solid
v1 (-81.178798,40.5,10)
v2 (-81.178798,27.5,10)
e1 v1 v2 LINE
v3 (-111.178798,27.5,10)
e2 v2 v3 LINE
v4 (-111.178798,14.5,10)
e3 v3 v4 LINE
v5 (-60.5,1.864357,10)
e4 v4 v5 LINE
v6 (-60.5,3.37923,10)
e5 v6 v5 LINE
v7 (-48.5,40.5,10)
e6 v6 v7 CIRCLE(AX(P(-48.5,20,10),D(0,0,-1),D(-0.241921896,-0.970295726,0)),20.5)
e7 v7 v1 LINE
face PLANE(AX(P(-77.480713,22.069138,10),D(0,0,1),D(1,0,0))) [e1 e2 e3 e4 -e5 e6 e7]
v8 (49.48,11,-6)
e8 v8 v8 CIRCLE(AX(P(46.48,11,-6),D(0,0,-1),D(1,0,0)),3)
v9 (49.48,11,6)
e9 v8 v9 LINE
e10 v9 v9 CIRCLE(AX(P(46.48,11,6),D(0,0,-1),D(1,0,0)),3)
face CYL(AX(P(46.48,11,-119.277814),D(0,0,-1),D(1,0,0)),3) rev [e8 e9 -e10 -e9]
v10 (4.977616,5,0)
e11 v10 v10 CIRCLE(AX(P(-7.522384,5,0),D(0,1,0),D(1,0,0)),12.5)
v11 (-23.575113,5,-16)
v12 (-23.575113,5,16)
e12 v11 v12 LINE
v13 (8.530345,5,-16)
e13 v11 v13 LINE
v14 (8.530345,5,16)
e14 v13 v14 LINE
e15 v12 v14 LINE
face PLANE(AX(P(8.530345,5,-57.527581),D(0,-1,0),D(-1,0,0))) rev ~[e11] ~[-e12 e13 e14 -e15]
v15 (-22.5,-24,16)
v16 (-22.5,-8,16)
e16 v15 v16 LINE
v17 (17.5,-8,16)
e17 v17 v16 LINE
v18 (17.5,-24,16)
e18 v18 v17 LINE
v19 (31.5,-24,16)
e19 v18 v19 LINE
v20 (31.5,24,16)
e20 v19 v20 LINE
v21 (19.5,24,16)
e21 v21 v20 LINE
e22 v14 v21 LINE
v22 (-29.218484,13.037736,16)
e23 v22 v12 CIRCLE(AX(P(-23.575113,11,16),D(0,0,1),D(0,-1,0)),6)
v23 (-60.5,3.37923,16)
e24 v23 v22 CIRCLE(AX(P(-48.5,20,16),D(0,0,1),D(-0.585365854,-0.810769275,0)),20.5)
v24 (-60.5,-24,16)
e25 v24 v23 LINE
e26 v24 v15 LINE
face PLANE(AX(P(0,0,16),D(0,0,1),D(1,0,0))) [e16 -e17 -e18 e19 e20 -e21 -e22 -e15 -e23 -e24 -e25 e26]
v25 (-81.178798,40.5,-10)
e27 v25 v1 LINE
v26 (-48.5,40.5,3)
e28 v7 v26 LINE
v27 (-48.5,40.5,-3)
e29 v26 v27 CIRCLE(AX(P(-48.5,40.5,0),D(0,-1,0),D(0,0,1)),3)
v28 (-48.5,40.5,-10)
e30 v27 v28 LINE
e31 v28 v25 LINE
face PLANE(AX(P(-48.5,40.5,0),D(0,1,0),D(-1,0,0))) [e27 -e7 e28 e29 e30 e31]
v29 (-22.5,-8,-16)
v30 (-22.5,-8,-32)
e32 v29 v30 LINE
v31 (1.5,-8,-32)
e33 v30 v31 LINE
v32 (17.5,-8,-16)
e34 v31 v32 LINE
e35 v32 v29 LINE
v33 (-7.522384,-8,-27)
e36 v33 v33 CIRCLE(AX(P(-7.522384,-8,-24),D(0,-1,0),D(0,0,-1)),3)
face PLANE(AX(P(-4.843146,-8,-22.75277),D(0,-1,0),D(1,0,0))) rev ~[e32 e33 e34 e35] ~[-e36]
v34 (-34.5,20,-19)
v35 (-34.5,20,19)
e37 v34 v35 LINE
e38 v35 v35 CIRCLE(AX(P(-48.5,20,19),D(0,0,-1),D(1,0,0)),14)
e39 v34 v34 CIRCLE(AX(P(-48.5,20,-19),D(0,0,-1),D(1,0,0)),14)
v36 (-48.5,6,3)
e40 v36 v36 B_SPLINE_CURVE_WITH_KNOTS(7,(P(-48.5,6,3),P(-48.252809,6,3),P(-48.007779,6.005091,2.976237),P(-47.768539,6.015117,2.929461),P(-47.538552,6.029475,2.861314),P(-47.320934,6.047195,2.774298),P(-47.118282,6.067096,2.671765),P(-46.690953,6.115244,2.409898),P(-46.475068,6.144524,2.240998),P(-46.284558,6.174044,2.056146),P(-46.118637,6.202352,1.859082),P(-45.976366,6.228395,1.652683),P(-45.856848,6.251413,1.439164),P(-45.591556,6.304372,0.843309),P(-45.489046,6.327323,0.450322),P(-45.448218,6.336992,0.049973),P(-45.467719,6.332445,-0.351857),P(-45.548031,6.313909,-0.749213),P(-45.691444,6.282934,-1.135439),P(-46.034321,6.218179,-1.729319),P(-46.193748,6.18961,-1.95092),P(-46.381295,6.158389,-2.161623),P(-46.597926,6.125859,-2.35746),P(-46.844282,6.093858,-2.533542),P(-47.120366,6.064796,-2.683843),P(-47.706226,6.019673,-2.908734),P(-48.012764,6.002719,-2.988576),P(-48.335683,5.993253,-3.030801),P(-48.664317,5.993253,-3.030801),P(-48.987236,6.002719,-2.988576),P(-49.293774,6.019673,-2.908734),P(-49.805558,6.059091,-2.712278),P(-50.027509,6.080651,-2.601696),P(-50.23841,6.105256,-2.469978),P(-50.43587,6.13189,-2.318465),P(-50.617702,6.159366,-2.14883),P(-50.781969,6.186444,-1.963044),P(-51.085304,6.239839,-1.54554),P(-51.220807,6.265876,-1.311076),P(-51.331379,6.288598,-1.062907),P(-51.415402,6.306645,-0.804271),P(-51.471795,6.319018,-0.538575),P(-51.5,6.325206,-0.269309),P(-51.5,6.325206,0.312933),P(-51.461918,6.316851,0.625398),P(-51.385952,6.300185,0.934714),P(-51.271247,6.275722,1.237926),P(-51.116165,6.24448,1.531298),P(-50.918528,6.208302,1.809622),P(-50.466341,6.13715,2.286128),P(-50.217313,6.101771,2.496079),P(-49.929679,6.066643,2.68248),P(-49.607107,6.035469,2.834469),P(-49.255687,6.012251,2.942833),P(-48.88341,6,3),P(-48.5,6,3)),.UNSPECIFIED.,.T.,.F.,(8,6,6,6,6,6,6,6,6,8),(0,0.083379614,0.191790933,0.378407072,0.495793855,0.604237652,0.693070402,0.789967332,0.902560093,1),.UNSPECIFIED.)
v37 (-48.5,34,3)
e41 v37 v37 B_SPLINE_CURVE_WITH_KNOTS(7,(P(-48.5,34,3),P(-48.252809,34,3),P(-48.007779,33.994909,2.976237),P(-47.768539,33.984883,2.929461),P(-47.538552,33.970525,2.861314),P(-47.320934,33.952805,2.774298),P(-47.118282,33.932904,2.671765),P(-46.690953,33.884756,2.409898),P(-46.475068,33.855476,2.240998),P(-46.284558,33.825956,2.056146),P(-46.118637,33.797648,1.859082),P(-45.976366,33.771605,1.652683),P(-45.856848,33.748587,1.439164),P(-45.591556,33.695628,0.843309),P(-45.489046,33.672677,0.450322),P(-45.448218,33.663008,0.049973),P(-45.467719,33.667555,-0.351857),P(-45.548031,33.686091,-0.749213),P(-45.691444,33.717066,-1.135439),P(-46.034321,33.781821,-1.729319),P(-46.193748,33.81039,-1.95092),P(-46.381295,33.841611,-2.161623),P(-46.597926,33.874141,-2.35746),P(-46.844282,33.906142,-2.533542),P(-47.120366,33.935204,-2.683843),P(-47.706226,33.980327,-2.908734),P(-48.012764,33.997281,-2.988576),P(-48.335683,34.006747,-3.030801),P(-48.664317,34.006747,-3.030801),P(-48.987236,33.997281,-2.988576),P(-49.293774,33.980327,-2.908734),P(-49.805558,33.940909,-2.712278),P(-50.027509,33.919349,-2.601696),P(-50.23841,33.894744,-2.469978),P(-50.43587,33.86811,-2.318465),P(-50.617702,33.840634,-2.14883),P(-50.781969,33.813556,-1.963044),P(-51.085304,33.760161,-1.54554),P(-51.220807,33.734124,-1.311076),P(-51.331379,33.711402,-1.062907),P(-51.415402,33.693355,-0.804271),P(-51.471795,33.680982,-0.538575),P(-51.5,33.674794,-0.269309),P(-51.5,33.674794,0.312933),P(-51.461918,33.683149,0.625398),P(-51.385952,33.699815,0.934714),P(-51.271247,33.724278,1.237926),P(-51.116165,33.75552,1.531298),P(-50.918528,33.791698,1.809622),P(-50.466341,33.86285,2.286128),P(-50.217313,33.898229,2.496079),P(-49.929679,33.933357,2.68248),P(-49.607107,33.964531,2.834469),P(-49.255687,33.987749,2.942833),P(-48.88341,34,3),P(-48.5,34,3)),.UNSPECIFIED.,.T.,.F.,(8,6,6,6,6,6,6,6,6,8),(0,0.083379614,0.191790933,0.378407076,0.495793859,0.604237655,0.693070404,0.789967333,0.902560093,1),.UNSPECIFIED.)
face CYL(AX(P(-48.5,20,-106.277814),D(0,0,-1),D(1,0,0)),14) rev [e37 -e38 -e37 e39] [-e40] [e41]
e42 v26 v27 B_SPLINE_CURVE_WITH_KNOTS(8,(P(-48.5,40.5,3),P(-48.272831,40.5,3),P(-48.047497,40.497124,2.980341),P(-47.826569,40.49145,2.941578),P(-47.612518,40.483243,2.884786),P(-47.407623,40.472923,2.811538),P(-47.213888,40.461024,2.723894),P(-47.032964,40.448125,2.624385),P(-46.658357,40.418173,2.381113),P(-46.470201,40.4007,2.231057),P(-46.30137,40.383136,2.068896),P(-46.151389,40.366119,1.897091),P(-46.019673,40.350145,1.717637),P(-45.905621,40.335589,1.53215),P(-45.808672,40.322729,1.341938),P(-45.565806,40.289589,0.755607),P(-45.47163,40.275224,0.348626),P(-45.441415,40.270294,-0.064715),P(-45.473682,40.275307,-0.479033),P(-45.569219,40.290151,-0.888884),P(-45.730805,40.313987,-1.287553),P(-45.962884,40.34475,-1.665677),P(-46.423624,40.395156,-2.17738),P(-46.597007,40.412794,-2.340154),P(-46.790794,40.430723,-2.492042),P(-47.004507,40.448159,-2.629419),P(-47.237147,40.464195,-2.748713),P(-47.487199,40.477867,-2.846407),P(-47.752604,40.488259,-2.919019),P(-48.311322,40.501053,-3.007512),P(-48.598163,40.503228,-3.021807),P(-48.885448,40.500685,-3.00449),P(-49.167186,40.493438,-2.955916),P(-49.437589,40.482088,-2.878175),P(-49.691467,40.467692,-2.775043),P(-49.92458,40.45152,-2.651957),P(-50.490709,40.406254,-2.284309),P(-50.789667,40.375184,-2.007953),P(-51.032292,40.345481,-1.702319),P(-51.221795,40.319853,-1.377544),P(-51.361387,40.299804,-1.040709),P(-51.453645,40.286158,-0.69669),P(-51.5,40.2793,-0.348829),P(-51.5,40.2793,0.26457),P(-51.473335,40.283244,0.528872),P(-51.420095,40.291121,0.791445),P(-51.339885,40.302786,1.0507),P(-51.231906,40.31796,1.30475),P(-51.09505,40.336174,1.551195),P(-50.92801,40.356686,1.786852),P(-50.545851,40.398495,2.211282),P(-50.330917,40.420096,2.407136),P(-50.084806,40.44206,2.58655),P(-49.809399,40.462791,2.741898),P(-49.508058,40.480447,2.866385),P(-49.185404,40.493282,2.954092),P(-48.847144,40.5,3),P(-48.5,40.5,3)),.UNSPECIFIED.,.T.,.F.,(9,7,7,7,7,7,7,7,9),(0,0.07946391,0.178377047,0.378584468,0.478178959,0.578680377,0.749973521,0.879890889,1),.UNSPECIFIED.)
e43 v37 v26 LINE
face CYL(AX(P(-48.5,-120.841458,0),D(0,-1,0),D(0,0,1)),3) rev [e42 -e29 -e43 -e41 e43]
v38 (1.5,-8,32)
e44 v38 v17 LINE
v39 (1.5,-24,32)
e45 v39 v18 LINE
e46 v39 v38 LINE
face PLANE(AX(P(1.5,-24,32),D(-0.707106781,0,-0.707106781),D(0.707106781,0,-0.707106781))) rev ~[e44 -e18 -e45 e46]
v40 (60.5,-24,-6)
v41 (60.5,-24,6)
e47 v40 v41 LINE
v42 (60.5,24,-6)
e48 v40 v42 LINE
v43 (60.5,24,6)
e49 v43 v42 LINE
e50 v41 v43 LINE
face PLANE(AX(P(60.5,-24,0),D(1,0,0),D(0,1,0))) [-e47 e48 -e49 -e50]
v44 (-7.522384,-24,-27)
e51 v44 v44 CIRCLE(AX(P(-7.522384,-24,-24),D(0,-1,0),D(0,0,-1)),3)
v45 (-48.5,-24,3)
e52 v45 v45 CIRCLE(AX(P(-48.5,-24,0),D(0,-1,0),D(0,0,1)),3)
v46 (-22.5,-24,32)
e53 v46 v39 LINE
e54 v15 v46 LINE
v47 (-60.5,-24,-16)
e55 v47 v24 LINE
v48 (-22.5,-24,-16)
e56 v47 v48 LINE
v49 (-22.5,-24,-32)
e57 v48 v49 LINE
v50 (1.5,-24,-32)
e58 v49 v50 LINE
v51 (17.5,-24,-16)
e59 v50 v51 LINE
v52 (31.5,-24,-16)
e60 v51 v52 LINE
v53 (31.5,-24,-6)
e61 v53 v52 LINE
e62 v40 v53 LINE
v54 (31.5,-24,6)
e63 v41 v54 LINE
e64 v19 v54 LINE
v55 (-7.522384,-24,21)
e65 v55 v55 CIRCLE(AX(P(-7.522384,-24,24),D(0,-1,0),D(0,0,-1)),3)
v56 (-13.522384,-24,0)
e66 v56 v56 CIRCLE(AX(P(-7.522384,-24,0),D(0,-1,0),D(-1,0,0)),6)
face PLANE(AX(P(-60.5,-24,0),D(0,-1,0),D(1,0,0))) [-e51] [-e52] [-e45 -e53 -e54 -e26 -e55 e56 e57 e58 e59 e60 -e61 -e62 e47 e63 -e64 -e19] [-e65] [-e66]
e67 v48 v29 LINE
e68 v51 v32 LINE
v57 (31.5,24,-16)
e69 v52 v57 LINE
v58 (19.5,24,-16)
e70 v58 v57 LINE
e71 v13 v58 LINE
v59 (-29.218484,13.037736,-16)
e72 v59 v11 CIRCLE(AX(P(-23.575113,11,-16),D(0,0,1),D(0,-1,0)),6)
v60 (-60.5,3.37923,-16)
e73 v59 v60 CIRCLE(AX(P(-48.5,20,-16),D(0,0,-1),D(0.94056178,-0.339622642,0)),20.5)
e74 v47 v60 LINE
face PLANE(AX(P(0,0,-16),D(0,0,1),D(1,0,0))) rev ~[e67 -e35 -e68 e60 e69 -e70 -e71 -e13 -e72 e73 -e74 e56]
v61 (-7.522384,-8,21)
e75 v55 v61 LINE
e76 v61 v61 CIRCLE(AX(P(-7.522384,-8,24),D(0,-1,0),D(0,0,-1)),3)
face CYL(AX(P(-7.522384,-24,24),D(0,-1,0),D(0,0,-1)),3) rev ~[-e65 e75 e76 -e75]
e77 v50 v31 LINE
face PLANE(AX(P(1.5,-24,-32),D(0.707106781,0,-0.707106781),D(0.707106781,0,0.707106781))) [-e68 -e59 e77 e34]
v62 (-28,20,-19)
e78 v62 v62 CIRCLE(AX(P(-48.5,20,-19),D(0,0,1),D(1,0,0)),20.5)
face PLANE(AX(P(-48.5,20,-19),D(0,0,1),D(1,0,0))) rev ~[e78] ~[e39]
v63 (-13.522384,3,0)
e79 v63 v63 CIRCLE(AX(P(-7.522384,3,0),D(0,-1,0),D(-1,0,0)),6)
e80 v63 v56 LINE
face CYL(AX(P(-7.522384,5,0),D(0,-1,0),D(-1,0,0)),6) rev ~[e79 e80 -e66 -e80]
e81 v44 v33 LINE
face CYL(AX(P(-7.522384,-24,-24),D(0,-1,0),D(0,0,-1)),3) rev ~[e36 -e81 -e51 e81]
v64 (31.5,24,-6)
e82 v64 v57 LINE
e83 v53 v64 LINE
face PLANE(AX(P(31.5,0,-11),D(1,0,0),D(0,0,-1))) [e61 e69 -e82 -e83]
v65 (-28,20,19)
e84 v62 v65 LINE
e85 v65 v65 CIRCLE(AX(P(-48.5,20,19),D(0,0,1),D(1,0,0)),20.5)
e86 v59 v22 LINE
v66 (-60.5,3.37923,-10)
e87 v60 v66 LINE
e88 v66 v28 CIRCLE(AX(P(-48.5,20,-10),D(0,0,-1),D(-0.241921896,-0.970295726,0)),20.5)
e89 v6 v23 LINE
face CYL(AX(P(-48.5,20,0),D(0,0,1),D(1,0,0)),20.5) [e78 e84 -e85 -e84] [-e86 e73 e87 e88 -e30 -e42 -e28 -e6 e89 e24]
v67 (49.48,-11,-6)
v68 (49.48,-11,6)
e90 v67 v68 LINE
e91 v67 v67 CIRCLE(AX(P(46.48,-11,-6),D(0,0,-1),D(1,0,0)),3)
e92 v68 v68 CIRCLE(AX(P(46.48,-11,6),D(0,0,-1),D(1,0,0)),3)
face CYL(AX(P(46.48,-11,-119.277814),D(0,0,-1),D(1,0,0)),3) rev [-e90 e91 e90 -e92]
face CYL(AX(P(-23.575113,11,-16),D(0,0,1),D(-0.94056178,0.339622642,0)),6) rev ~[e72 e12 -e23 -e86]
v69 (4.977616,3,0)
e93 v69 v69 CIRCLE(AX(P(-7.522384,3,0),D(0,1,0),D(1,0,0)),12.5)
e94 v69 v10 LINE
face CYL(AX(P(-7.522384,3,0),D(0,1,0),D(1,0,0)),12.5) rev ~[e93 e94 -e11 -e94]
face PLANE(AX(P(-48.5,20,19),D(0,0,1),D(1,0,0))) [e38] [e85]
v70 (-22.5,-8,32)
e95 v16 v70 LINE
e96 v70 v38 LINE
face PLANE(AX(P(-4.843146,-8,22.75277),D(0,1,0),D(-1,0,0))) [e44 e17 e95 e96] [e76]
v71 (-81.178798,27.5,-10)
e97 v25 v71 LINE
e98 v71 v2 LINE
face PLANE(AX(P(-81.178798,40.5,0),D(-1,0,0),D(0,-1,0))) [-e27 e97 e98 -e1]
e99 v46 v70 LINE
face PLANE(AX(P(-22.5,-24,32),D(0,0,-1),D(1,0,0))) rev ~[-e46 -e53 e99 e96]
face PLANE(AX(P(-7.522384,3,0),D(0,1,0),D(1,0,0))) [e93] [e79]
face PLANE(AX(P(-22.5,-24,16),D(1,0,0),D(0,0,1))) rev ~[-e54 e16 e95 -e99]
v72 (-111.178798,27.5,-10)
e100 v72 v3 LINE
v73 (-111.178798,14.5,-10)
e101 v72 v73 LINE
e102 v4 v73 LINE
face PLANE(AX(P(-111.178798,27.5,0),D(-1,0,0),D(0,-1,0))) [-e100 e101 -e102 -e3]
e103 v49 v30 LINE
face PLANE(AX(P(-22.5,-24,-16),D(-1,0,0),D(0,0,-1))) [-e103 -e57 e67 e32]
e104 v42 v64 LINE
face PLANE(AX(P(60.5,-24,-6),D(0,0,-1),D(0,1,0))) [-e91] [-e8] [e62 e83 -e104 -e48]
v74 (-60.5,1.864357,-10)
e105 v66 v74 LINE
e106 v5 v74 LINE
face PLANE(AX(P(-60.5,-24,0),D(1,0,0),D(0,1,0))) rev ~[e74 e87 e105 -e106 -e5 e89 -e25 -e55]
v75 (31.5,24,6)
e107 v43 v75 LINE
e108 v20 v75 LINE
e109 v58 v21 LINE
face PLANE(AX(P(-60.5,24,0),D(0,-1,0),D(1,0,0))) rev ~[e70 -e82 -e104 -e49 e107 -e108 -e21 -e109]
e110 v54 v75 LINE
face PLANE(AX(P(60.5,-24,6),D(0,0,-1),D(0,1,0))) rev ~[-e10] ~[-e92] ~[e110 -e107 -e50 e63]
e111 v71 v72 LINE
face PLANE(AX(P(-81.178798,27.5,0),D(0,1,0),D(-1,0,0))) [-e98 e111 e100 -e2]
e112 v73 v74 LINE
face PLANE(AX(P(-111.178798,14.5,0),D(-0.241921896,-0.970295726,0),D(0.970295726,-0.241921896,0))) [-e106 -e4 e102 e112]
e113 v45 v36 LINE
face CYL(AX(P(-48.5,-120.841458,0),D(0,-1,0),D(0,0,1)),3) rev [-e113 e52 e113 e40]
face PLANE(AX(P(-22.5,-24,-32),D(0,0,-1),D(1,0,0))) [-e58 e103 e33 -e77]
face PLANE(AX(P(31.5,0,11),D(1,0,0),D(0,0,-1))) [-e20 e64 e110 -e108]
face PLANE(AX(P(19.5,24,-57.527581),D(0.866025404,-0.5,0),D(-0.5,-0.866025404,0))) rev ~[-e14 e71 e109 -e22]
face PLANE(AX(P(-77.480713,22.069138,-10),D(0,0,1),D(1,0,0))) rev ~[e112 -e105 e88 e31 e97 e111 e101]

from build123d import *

# Parameters (mm, degrees)
BASE_BLOCK_SKETCH_W                = 121
BASE_BLOCK_SKETCH_H                = 48
BASE_BLOCK_121X48_DEPTH            = 16
BASE_STEP_SKETCH_W                 = 10
BASE_STEP_SKETCH_H                 = 48
BASE_STEP_CUT_DEPTH                = 29
ANGLED_RELIEF_CUT_30DEG_DEPTH      = 73.527580961
ANGLED_RELIEF_CUT_30DEG_DEPTH_BACK = 73.527580961
PIVOT_BOSS_SKETCH_R                = 20.5
PIVOT_BOSS_44_DEPTH                = 19
PIVOT_BOSS_FILLET_R6_R             = 6
CLAMP_TAB_DEPTH                    = 10
TAB_PIN_HOLE_6_DEPTH               = 120.841457826
TAB_PIN_HOLE_6_DEPTH_BACK          = 120.841457826
TAB_PIN_HOLE_SKETCH_R              = 3
PIVOT_BORE_28_DEPTH                = 125.277813908
PIVOT_BORE_28_DEPTH_BACK           = 125.277813908
PIVOT_BORE_SKETCH_R                = 14
COUNTERBORED_HOLE_12_D             = 12
COUNTERBORED_HOLE_12_CBORE_D       = 25
COUNTERBORED_HOLE_12_CBORE_DEPTH   = 2
MOUNTING_FLANGE_SKETCH_R           = 3
MOUNTING_FLANGE_DEPTH              = 16
END_SLOT_CUT_DEPTH                 = 125.277813877
END_SLOT_CUT_DEPTH_BACK            = 125.277813877
END_SLOT_SKETCH_R                  = 3


with BuildPart() as part:
    # Base Block Sketch → Base Block 121x48 (new, symmetric)
    with BuildSketch(Plane.XY):
        Rectangle(BASE_BLOCK_SKETCH_W, BASE_BLOCK_SKETCH_H)
    extrude(amount=BASE_BLOCK_121X48_DEPTH, both=True)

    # Base Step Sketch → Base Step Cut (cut)
    with BuildSketch(Plane(origin=(60.5, 0, 0), x_dir=(0, 0, -1), z_dir=(1, 0, 0))):
        with Locations((-11, 0)):
            Rectangle(BASE_STEP_SKETCH_W, BASE_STEP_SKETCH_H)
        with Locations((11, 0)):
            Rectangle(BASE_STEP_SKETCH_W, BASE_STEP_SKETCH_H)
    extrude(amount=-BASE_STEP_CUT_DEPTH, mode=Mode.SUBTRACT)

    # Angled Relief Sketch → Angled Relief Cut 30deg (cut, two sides: drawn at the far end of the back side and taken through both)
    with BuildSketch(Plane.XY.offset(16).offset(-ANGLED_RELIEF_CUT_30DEG_DEPTH_BACK)):
        Polygon((19.5, 24), (8.530344885, 5), (-40, 5), (-40, 24), align=None)
    extrude(amount=ANGLED_RELIEF_CUT_30DEG_DEPTH + ANGLED_RELIEF_CUT_30DEG_DEPTH_BACK, mode=Mode.SUBTRACT)

    # Pivot Boss Sketch → Pivot Boss Ø44 (add, symmetric)
    with BuildSketch(Plane.XY):
        with Locations((-48.5, 20)):
            Circle(PIVOT_BOSS_SKETCH_R)
    extrude(amount=PIVOT_BOSS_44_DEPTH, both=True)

    # Pivot Boss Fillet R6
    pivot_boss_fillet_r6_edges = [part.edges().sort_by_distance(p)[0] for p in [
        (-34.526811388, 5, 0),
    ]]
    fillet(pivot_boss_fillet_r6_edges, radius=PIVOT_BOSS_FILLET_R6_R)

    # Clamp Tab Sketch → Clamp Tab (add, symmetric)
    with BuildSketch(Plane.XY):
        with BuildLine():
            Line((-48.5, 40.5), (-81.178797502, 40.5))
            Line((-81.178797502, 40.5), (-81.178797502, 27.5))
            Line((-81.178797502, 27.5), (-111.178797502, 27.5))
            Line((-111.178797502, 27.5), (-111.178797502, 14.5))
            Line((-111.178797502, 14.5), (-53.45939886, 0.108937611))
            ThreePointArc((-53.45939886, 0.108937611), (-68.847196109, 22.49832154), (-48.5, 40.5))
        make_face()
    extrude(amount=CLAMP_TAB_DEPTH, both=True)

    # Tab Pin Hole Sketch → Tab Pin Hole Ø6 (cut, two sides: drawn at the far end of the back side and taken through both)
    with BuildSketch(Plane(origin=(0, 0, 0), x_dir=(1, 0, 0), z_dir=(0, 1, 0)).offset(-TAB_PIN_HOLE_6_DEPTH_BACK)):
        with Locations(Location((-48.5, 0, 0), (0, 0, 270))):
            Circle(TAB_PIN_HOLE_SKETCH_R)
    extrude(amount=TAB_PIN_HOLE_6_DEPTH + TAB_PIN_HOLE_6_DEPTH_BACK, mode=Mode.SUBTRACT)

    # Pivot Bore Sketch → Pivot Bore Ø28 (cut, two sides: drawn at the far end of the back side and taken through both)
    with BuildSketch(Plane.XY.offset(19).offset(-PIVOT_BORE_28_DEPTH_BACK)):
        with Locations((-48.5, 20)):
            Circle(PIVOT_BORE_SKETCH_R)
    extrude(amount=PIVOT_BORE_28_DEPTH + PIVOT_BORE_28_DEPTH_BACK, mode=Mode.SUBTRACT)

    # Counterbored Hole Ø12 (through all)
    with Locations(Plane(origin=(0, 5, 0), x_dir=(1, 0, 0), z_dir=(0, 1, 0))):
        with Locations((-7.522383977, 0)):
            CounterBoreHole(COUNTERBORED_HOLE_12_D / 2, COUNTERBORED_HOLE_12_CBORE_D / 2, COUNTERBORED_HOLE_12_CBORE_DEPTH)

    # Mounting Flange Sketch → Mounting Flange (add)
    # profile 1 of 2: a face of its own
    with BuildSketch(Plane.XZ.offset(24)):
        Polygon((-22.5, -16), (-22.5, -32), (1.5, -32), (17.5, -16), align=None)
        with Locations(Location((-7.522383977, -24, 0), (0, 0, 270))):
            Circle(MOUNTING_FLANGE_SKETCH_R, mode=Mode.SUBTRACT)
    # profile 2 of 2: a face of its own
    with BuildSketch(Plane.XZ.offset(24)):
        Polygon((17.5, 16), (-22.5, 16), (-22.5, 32), (1.5, 32), align=None)
        with Locations(Location((-7.522383977, 24, 0), (0, 0, 270))):
            Circle(MOUNTING_FLANGE_SKETCH_R, mode=Mode.SUBTRACT)
    extrude(amount=-MOUNTING_FLANGE_DEPTH)

    # End Slot Sketch → End Slot Cut (cut, two sides: drawn at the far end of the back side and taken through both)
    with BuildSketch(Plane.XY.offset(6).offset(-END_SLOT_CUT_DEPTH_BACK)):
        with Locations((46.48, 11)):
            Circle(END_SLOT_SKETCH_R)
        with Locations((46.48, -11)):
            Circle(END_SLOT_SKETCH_R)
    extrude(amount=END_SLOT_CUT_DEPTH + END_SLOT_CUT_DEPTH_BACK, mode=Mode.SUBTRACT)


solid = part.part
